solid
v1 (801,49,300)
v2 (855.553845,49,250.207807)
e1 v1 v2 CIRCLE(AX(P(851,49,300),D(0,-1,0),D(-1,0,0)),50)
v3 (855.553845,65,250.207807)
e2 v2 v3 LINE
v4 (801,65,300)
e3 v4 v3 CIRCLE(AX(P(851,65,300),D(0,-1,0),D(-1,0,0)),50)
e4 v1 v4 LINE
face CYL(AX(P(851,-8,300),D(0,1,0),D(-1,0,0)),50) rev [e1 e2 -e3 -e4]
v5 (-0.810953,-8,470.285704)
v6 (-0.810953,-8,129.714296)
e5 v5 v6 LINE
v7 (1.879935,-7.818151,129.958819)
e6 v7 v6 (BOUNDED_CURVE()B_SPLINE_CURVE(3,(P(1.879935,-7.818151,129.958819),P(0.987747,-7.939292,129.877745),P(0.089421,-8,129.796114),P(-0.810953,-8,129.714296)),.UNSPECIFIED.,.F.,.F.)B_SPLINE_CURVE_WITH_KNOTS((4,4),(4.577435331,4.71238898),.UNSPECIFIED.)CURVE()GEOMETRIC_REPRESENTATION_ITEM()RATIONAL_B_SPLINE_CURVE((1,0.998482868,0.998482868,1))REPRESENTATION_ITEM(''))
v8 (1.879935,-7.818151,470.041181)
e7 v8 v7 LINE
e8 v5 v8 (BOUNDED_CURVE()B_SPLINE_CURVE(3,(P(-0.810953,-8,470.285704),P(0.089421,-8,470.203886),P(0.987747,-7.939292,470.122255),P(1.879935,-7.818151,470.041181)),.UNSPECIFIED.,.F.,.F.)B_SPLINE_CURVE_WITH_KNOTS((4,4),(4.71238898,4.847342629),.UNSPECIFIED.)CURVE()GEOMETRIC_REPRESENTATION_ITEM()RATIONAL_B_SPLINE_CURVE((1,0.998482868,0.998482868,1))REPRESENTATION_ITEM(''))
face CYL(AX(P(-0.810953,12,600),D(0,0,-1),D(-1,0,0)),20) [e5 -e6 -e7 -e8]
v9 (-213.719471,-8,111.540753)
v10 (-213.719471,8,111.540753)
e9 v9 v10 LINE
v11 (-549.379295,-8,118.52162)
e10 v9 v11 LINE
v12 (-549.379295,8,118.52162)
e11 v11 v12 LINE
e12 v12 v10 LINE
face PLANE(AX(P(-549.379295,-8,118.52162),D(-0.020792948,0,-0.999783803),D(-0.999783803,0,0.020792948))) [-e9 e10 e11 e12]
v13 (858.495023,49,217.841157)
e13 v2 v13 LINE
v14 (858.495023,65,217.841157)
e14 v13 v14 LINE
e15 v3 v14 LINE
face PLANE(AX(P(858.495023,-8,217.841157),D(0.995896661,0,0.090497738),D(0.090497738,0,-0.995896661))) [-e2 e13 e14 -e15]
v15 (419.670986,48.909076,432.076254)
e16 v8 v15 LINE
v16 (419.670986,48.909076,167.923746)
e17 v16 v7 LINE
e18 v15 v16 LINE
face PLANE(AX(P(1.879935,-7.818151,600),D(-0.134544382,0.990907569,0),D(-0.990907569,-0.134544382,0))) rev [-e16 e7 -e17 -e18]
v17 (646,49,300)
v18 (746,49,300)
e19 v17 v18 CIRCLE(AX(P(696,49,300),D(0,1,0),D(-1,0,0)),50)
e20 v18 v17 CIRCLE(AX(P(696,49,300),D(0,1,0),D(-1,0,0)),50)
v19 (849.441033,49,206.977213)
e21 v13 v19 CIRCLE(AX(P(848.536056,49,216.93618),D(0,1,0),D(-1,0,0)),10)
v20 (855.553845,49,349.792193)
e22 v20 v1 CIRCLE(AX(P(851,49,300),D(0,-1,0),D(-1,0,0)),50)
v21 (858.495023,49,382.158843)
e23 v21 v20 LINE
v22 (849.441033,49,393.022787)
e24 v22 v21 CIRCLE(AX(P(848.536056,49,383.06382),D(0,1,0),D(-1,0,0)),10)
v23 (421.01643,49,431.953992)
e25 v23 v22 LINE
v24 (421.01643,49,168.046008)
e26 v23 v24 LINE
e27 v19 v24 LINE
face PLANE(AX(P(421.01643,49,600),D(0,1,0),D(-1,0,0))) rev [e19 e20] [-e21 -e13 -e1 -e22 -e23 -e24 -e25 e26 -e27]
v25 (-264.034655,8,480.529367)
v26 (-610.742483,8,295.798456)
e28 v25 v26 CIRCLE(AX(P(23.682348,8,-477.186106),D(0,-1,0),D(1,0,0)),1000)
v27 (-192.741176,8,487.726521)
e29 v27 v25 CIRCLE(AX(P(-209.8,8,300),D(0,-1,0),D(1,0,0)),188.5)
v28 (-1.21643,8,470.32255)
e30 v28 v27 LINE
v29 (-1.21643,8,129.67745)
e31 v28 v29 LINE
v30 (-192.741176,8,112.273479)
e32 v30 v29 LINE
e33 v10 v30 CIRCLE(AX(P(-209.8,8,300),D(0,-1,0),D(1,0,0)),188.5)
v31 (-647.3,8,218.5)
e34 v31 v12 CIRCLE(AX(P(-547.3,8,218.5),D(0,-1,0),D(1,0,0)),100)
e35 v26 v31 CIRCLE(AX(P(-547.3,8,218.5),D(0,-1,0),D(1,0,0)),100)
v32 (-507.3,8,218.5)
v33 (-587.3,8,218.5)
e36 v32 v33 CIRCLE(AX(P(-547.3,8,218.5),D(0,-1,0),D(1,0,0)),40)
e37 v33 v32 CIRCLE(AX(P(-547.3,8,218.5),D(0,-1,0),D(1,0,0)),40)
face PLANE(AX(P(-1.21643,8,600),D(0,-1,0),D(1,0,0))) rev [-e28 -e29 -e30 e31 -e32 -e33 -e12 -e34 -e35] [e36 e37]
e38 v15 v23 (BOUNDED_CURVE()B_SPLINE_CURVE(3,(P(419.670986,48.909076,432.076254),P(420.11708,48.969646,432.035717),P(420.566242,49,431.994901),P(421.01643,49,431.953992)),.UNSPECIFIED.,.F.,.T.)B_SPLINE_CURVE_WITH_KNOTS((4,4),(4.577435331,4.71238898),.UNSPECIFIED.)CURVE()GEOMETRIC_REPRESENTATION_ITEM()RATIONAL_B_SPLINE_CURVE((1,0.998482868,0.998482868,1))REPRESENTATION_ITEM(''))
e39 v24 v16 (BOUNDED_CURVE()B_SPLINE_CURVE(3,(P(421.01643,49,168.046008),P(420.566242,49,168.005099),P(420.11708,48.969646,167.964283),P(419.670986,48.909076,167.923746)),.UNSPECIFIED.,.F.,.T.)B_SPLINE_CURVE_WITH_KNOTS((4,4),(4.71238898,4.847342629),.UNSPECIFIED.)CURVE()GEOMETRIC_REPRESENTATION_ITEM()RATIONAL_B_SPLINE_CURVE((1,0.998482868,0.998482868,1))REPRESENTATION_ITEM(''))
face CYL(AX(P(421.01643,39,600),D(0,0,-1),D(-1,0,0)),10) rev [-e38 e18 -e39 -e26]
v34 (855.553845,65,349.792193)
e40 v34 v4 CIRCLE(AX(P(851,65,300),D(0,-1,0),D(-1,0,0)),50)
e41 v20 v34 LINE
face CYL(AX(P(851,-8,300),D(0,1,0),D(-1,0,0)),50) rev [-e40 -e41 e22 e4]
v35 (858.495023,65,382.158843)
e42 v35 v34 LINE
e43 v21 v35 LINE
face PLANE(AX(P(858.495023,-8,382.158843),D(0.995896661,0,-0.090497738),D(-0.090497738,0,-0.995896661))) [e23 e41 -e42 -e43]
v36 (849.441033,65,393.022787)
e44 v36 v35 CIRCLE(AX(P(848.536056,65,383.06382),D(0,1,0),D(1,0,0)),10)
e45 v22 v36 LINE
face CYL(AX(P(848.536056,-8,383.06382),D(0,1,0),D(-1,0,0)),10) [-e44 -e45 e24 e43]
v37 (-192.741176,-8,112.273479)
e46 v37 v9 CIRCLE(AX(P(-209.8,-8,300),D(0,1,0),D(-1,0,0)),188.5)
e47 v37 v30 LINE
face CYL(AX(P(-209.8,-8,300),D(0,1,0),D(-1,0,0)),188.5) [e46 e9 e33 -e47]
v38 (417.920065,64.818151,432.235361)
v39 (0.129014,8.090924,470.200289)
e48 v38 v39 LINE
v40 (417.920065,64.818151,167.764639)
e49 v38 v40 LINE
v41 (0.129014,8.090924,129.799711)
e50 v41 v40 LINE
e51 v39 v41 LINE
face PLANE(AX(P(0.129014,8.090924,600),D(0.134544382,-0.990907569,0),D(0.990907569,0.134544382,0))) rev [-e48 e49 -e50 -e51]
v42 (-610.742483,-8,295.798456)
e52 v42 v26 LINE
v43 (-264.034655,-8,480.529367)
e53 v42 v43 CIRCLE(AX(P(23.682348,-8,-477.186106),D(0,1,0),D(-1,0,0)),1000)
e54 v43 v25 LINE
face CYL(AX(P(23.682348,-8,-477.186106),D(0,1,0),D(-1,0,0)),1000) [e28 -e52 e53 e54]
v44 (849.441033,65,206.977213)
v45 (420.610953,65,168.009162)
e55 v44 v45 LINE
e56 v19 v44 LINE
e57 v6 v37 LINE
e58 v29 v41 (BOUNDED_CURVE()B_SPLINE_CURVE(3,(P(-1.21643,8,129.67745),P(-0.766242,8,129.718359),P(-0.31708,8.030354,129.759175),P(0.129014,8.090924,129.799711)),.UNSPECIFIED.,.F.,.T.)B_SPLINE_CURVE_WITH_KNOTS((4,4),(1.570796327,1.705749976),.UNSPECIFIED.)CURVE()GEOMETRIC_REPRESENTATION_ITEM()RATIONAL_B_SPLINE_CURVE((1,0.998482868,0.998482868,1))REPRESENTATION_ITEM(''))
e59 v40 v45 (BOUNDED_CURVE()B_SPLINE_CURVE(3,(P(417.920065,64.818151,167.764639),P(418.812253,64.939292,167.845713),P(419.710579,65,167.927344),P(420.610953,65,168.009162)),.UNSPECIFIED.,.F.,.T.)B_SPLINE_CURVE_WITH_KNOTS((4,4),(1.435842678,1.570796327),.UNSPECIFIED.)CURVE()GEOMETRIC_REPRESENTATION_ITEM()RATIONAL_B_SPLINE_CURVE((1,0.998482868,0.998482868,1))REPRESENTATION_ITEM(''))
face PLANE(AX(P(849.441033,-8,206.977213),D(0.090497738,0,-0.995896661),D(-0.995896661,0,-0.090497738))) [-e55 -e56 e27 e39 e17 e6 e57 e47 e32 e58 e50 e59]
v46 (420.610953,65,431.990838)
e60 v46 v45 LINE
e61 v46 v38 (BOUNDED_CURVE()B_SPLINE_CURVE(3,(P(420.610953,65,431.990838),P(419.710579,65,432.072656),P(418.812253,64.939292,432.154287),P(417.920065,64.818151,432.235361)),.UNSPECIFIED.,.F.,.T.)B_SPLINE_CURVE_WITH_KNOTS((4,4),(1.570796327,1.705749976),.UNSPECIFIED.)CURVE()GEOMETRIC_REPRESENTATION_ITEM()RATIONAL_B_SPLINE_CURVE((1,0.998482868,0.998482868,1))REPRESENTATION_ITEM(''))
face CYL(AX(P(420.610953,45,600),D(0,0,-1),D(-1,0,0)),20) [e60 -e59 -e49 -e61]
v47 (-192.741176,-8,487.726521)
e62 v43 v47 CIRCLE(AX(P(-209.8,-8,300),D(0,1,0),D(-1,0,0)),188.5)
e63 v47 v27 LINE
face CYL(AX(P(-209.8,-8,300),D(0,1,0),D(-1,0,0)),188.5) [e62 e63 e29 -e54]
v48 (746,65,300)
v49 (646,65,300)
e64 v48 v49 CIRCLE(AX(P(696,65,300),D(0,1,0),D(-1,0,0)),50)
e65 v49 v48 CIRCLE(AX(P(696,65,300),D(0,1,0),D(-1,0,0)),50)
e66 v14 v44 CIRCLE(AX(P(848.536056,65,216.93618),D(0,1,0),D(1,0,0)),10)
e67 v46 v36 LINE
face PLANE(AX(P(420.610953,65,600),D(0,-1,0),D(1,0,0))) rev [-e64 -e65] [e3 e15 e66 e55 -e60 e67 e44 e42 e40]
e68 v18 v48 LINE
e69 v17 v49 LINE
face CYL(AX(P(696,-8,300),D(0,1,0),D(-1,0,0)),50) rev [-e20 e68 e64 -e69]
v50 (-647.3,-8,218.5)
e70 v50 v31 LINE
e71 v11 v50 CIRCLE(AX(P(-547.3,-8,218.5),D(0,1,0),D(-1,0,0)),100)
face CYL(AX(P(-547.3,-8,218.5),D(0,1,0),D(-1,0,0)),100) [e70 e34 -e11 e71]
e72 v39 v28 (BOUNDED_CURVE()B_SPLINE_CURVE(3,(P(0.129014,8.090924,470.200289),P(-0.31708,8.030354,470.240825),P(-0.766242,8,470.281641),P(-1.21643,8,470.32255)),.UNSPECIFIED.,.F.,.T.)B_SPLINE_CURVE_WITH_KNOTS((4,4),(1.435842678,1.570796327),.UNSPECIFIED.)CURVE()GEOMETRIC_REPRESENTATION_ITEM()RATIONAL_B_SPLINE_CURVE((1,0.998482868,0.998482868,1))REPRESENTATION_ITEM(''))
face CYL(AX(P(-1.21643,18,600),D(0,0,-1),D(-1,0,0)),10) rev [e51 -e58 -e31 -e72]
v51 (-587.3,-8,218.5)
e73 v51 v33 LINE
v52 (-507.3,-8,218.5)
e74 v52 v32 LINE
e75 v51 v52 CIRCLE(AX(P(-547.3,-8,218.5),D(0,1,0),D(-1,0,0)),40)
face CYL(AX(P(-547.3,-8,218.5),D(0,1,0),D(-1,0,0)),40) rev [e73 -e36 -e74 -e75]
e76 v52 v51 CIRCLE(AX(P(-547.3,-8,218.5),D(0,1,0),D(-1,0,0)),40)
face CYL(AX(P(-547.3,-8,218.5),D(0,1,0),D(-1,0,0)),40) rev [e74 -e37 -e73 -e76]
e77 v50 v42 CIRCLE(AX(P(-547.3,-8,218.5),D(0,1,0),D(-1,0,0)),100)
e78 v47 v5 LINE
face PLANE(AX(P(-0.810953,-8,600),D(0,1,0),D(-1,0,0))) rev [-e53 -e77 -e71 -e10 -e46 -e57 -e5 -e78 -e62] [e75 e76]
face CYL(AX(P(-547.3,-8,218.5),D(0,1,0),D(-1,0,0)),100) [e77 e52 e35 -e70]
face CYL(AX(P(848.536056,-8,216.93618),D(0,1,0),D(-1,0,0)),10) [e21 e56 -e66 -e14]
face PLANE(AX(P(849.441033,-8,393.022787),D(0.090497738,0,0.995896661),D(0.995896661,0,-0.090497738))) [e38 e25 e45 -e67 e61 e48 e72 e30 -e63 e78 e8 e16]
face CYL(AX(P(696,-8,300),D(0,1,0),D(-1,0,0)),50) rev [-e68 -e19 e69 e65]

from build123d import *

# Parameters (mm, degrees)
BOSS_EXTRUDE1_DEPTH = 600
SKETCH4_OUTSIDE_W   = 1933.152
SKETCH4_OUTSIDE_H   = 942.352
SKETCH4_OUTSIDE_R   = 40
SKETCH4_OUTSIDE_R_2 = 50
CUT_EXTRUDE1_DEPTH  = 1121.500446229


with BuildPart() as part:
    # Sketch1 → Boss-Extrude1 (new body)
    with BuildSketch(Plane.XY):
        with BuildLine():
            Line((-1.216429586, 8), (-647.3, 8))
            Line((-647.3, 8), (-647.3, -8))
            Line((-647.3, -8), (-0.810953057, -8))
            ThreePointArc((-0.810953057, -8), (0.537559565, -7.954486055), (1.879934575, -7.818151371))
            Line((1.879934575, -7.818151371), (419.67098577, 48.909075685))
            ThreePointArc((419.67098577, 48.909075685), (420.342173275, 48.977243027), (421.016429586, 49))
            Line((421.016429586, 49), (943.5, 49))
            Line((943.5, 49), (943.5, 65))
            Line((943.5, 65), (420.610953057, 65))
            ThreePointArc((420.610953057, 65), (419.262440435, 64.954486055), (417.920065425, 64.818151371))
            Line((417.920065425, 64.818151371), (0.12901423, 8.090924315))
            ThreePointArc((0.12901423, 8.090924315), (-0.542173275, 8.022756973), (-1.216429586, 8))
        make_face()
    extrude(amount=BOSS_EXTRUDE1_DEPTH)

    # Sketch4 outside → Cut-Extrude1 (cut, through all)
    # profile 1 of 3: a face of its own
    with BuildSketch(Plane(origin=(0, 65, 0), x_dir=(1, 0, 0), z_dir=(0, 1, 0))):
        with Locations((148.1, -300)):
            Rectangle(SKETCH4_OUTSIDE_W, SKETCH4_OUTSIDE_H)
        with BuildLine():
            Line((849.441033389, -393.022786976), (-192.741176471, -487.726520609))
            ThreePointArc((-192.741176471, -487.726520609), (-228.733049722, -487.54676651), (-264.034655196, -480.529366519))
            ThreePointArc((-264.034655196, -480.529366519), (-446.549262984, -405.356942265), (-610.742483166, -295.798456192))
            ThreePointArc((-610.742483166, -295.798456192), (-641.798915546, -185.789833988), (-549.379294824, -118.521619672))
            Line((-549.379294824, -118.521619672), (-213.719470744, -111.540753082))
            ThreePointArc((-213.719470744, -111.540753082), (-203.220116273, -111.614875507), (-192.741176471, -112.273479391))
            Line((-192.741176471, -112.273479391), (849.441033389, -206.977213024))
            ThreePointArc((849.441033389, -206.977213024), (856.218024477, -210.53404245), (858.495022624, -217.84115701))
            Line((858.495022624, -217.84115701), (855.553845389, -250.207806915))
            ThreePointArc((855.553845389, -250.207806915), (801, -300), (855.553845389, -349.792193085))
            Line((855.553845389, -349.792193085), (858.495022624, -382.15884299))
            ThreePointArc((858.495022624, -382.15884299), (856.218024477, -389.46595755), (849.441033389, -393.022786976))
        make_face(mode=Mode.SUBTRACT)
    # profile 2 of 3: a face of its own
    with BuildSketch(Plane(origin=(0, 65, 0), x_dir=(1, 0, 0), z_dir=(0, 1, 0))):
        with Locations(Location((-547.3, -218.5, 0), (0, 0, 180))):
            Circle(SKETCH4_OUTSIDE_R)
    # profile 3 of 3: a face of its own
    with BuildSketch(Plane(origin=(0, 65, 0), x_dir=(1, 0, 0), z_dir=(0, 1, 0))):
        with Locations(Location((696, -300, 0), (0, 0, 180))):
            Circle(SKETCH4_OUTSIDE_R_2)
    extrude(amount=-CUT_EXTRUDE1_DEPTH, mode=Mode.SUBTRACT)


solid = part.part
